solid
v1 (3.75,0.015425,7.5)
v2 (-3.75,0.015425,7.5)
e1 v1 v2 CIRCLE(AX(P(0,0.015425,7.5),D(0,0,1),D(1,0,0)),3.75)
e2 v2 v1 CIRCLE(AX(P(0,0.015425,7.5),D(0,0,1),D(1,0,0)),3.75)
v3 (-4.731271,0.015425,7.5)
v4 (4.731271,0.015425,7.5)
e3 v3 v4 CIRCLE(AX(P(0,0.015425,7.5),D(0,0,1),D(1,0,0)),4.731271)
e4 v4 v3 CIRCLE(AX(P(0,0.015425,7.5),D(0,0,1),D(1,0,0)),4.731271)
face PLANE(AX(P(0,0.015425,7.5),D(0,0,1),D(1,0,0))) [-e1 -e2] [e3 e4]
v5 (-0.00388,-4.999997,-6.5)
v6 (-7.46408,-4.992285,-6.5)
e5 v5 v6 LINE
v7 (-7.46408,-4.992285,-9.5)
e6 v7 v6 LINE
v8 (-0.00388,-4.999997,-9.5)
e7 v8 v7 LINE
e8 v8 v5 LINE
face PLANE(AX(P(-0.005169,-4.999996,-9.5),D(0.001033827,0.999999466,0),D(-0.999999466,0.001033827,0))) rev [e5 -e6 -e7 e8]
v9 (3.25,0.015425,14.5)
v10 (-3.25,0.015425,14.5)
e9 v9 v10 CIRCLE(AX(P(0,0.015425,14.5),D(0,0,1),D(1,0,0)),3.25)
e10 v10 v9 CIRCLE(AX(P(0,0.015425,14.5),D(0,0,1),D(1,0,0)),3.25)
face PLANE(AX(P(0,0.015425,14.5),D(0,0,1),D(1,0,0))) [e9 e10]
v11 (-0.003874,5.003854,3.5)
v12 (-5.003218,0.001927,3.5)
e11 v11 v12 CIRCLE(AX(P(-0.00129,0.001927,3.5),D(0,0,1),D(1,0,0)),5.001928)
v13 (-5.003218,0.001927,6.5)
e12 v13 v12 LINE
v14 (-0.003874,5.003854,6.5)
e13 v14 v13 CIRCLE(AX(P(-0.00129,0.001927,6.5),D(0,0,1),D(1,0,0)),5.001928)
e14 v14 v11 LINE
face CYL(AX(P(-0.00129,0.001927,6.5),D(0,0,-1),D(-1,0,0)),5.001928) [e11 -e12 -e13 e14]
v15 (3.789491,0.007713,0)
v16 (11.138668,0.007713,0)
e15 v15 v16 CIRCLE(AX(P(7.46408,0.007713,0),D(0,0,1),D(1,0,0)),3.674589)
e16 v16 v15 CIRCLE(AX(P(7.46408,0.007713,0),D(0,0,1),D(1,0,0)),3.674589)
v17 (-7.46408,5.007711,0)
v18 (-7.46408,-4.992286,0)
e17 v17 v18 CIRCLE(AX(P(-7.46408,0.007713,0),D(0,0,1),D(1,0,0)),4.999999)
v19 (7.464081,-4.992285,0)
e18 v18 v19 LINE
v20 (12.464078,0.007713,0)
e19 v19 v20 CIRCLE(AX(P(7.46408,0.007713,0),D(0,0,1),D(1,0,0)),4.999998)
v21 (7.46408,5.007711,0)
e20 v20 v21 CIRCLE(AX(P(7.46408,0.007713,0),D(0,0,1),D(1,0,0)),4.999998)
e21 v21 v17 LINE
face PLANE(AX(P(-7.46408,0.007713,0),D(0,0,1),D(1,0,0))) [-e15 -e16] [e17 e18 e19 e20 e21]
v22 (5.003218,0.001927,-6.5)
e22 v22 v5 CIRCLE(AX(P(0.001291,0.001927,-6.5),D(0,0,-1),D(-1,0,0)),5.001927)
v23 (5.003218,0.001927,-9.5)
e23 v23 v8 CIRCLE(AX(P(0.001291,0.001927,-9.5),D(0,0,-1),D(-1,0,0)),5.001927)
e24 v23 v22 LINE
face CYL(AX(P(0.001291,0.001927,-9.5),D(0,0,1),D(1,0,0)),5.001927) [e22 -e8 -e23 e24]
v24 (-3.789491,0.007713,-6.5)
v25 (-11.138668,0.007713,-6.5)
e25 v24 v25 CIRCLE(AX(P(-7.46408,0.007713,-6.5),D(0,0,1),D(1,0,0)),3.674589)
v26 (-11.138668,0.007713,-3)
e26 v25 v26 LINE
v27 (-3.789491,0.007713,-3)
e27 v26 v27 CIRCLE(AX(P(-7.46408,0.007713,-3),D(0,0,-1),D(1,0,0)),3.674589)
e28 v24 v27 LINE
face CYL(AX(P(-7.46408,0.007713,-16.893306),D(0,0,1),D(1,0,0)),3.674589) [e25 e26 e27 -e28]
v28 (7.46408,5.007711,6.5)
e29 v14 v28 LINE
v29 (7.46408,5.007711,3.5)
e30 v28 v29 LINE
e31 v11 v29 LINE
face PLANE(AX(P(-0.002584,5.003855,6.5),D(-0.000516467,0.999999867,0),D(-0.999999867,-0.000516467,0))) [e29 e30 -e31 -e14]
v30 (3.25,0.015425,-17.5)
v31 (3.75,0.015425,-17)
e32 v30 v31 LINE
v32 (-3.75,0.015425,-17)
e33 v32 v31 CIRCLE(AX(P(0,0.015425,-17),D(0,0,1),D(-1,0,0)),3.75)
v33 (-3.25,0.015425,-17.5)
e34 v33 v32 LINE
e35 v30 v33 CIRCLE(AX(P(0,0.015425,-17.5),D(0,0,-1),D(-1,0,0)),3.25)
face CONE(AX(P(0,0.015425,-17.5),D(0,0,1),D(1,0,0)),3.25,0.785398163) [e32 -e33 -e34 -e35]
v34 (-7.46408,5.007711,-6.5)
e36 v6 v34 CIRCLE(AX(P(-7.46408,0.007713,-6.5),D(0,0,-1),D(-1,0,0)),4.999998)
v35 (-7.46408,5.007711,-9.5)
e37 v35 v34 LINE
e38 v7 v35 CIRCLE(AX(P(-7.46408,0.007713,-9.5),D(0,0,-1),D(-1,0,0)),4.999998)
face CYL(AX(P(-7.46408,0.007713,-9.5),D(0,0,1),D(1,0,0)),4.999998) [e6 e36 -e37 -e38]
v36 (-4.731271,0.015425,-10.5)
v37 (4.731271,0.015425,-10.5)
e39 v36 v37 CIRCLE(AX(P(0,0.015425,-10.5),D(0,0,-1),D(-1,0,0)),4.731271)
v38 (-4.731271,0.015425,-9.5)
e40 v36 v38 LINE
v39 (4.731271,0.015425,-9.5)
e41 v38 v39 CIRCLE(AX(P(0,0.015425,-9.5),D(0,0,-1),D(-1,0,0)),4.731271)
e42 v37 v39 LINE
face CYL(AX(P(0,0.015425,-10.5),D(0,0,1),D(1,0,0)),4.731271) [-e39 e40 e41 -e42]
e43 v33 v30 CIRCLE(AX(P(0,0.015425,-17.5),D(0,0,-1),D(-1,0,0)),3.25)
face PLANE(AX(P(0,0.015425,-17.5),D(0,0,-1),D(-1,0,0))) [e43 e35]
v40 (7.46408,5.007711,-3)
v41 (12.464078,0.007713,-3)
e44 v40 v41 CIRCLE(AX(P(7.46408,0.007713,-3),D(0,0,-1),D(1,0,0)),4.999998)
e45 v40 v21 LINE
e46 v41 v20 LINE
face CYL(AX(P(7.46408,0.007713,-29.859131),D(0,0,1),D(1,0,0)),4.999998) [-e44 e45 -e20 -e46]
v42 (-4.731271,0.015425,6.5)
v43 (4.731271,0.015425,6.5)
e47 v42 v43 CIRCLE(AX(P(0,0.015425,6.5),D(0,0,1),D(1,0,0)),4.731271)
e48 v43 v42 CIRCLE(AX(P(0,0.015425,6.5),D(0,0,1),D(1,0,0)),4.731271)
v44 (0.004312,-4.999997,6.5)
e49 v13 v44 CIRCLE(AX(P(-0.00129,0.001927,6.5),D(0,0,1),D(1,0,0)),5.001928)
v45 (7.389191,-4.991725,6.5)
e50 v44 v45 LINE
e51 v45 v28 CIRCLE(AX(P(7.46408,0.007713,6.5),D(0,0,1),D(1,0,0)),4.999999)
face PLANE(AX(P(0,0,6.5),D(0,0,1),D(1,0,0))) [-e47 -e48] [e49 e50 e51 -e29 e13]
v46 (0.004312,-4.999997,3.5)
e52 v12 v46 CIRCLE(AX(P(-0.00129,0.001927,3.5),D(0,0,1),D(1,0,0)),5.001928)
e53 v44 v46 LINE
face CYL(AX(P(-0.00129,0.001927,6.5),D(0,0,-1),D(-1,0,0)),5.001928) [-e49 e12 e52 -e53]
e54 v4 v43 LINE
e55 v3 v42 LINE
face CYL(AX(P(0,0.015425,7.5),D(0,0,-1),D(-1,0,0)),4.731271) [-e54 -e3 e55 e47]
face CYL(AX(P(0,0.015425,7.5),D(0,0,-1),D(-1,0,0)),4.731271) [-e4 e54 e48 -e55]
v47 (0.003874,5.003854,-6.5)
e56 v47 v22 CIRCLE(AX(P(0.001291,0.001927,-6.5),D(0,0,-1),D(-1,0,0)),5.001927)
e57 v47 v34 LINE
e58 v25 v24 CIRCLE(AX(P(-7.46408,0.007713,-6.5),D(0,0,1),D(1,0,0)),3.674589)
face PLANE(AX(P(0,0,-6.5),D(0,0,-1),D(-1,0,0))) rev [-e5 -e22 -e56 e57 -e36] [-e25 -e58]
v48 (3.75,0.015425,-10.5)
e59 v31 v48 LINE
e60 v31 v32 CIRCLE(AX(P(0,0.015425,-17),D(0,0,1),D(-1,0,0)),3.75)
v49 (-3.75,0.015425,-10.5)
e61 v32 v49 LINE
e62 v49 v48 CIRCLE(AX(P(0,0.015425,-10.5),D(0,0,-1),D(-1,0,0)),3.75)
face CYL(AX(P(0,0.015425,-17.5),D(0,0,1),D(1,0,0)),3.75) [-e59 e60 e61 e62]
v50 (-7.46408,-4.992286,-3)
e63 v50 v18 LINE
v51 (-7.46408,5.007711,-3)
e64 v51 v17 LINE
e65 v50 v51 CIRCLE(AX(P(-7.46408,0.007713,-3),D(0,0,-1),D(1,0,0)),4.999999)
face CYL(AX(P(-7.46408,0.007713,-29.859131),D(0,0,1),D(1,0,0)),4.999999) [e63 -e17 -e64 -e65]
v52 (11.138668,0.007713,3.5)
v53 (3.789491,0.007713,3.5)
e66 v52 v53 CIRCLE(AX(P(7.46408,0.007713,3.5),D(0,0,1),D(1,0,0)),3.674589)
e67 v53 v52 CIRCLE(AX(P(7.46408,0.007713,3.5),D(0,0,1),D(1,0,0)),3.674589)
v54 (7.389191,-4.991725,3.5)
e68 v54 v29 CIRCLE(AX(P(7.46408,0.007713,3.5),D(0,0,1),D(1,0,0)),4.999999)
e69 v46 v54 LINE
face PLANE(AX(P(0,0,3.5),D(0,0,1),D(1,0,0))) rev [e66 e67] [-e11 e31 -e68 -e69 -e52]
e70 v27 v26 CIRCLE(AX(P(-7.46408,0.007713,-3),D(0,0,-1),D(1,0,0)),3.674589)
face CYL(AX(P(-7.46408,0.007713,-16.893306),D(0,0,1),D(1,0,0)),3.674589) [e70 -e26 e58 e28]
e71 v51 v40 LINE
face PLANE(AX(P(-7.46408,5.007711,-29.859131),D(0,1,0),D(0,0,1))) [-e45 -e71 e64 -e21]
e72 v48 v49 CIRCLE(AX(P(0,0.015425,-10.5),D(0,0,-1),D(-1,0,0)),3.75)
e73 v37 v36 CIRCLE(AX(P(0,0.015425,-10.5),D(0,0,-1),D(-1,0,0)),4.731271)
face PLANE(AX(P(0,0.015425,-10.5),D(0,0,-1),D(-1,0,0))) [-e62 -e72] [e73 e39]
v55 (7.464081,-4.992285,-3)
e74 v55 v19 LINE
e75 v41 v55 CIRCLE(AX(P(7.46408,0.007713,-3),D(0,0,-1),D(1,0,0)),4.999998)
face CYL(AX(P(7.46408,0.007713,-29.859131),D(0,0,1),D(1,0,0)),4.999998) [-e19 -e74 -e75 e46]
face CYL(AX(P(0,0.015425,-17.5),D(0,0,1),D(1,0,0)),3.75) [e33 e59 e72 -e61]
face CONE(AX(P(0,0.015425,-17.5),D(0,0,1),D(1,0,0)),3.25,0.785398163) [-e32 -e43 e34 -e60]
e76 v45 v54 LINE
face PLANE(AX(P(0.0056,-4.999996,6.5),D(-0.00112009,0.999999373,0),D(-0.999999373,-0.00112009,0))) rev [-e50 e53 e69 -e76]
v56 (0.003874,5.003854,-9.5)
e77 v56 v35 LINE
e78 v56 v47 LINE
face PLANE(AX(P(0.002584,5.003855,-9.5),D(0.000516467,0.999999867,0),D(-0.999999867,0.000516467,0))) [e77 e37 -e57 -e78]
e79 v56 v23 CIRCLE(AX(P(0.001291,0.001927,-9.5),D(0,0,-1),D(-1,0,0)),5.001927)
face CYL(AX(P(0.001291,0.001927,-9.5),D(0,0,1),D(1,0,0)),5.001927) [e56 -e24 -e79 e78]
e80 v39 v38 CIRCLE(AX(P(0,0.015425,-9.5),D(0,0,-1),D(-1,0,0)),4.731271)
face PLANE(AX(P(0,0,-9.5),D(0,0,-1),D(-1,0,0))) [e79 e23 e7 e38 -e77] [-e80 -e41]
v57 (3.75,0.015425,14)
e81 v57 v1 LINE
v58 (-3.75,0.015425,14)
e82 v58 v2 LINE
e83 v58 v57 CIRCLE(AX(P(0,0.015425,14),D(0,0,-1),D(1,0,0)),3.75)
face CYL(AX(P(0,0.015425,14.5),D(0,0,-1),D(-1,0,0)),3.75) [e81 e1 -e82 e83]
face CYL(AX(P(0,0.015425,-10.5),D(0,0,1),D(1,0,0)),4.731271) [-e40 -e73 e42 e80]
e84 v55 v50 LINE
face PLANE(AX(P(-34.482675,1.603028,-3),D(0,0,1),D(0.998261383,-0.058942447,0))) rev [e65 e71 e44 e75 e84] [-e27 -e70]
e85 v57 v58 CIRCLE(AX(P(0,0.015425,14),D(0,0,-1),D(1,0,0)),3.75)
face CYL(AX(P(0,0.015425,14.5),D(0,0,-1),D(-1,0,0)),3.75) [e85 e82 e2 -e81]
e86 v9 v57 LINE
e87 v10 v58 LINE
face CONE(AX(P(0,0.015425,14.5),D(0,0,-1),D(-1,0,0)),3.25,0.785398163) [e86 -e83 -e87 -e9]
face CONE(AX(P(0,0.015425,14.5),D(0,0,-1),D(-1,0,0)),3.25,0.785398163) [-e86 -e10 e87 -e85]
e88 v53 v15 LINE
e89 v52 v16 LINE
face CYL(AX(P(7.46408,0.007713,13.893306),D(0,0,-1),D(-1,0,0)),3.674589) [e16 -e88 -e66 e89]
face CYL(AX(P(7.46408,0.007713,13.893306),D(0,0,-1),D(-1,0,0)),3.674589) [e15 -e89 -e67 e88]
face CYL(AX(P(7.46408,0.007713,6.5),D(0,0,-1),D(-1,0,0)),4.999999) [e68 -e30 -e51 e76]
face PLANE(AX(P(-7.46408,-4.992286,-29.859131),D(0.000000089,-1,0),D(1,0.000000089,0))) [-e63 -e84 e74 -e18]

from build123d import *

# Parameters (mm, degrees)
BOSS_EXTRUDE7_DEPTH  = 3
SKETCH7_R            = 3.674588618
BOSS_EXTRUDE8_DEPTH  = 3.5
SKETCH8_R            = 3.674588618
BOSS_EXTRUDE9_DEPTH  = 3.5
SKETCH9_R            = 3.674588618
BOSS_EXTRUDE10_DEPTH = 3
SKETCH10_R           = 3.674588618
BOSS_EXTRUDE11_DEPTH = 3
SKETCH11_R           = 4.731271099
BOSS_EXTRUDE12_DEPTH = 1
SKETCH12_R           = 3.75
BOSS_EXTRUDE13_DEPTH = 7
BOSS_EXTRUDE14_START = 1
SKETCH13_R           = 4.731271099
BOSS_EXTRUDE14_DEPTH = 1
BOSS_EXTRUDE15_START = 7
SKETCH14_R           = 3.75
BOSS_EXTRUDE15_DEPTH = 7
CHAMFER1_SIZE        = 0.5


with BuildPart() as part:
    # Sketch1 → Boss-Extrude7 (new body)
    with BuildSketch(Plane.XY):
        with BuildLine():
            Line((-7.464079644, 5.007711231), (7.464079644, 5.007711231))
            ThreePointArc((7.464079644, 5.007711231), (12.46407809, 0.007713678), (7.464080538, -4.992284768))
            Line((7.464080538, -4.992284768), (-7.464079644, -4.992286102))
            ThreePointArc((-7.464079644, -4.992286102), (-12.464078311, 0.007712565), (-7.464079644, 5.007711231))
        make_face()
    extrude(amount=-BOSS_EXTRUDE7_DEPTH)

    # Sketch7 → Boss-Extrude8 (add)
    with BuildSketch(Plane(origin=(0, 0, -3), x_dir=(-1, 0, 0), z_dir=(0, 0, -1))):
        with Locations(Location((7.464079644, 0.007712565, 0), (0, 0, 180))):
            Circle(SKETCH7_R)
    extrude(amount=BOSS_EXTRUDE8_DEPTH)

    # Sketch8 → Boss-Extrude9 (add)
    with BuildSketch(Plane.XY):
        with Locations((7.464079644, 0.007712565)):
            Circle(SKETCH8_R)
    extrude(amount=BOSS_EXTRUDE9_DEPTH)

    # Sketch9 → Boss-Extrude10 (add)
    # profile 1 of 2: a face of its own
    with BuildSketch(Plane(origin=(0, 0, -6.5), x_dir=(-1, 0, 0), z_dir=(0, 0, -1))):
        with BuildLine():
            Line((7.458914982, 5.007708564), (-0.003874001, 5.003854283))
            ThreePointArc((-0.003874001, 5.003854283), (-5.003216645, -0.001949753), (0.003880454, -4.999997327))
            Line((0.003880454, -4.999997327), (7.464079644, -4.992284768))
            ThreePointArc((7.464079644, -4.992284768), (12.464077644, 0.007713232), (7.464079644, 5.007711231))
            Line((7.464079644, 5.007711231), (7.458914982, 5.007708564))
        make_face()
        with Locations(Location((7.464079644, 0.007712565, 0), (0, 0, 180))):
            Circle(SKETCH9_R, mode=Mode.SUBTRACT)
    # profile 2 of 2: a face of its own
    with BuildSketch(Plane(origin=(0, 0, -6.5), x_dir=(-1, 0, 0), z_dir=(0, 0, -1))):
        with Locations(Location((7.464079644, 0.007712565, 0), (0, 0, 180))):
            Circle(SKETCH9_R)
    extrude(amount=BOSS_EXTRUDE10_DEPTH)

    # Sketch10 → Boss-Extrude11 (add)
    # profile 1 of 2: a face of its own
    with BuildSketch(Plane.XY.offset(3.5)):
        with BuildLine():
            ThreePointArc((-0.003873651, 5.003854283), (-5.003216178, -0.00216555), (0.004312288, -4.999996973))
            Line((0.004312288, -4.999996973), (7.3891908, -4.991725236))
            ThreePointArc((7.3891908, -4.991725236), (12.463938092, -0.029732908), (7.464079644, 5.007711231))
            Line((7.464079644, 5.007711231), (7.458914981, 5.007708564))
            Line((7.458914981, 5.007708564), (-0.003873651, 5.003854283))
        make_face()
        with Locations((7.464079644, 0.007712565)):
            Circle(SKETCH10_R, mode=Mode.SUBTRACT)
    # profile 2 of 2: a face of its own
    with BuildSketch(Plane.XY.offset(3.5)):
        with Locations((7.464079644, 0.007712565)):
            Circle(SKETCH10_R)
    extrude(amount=BOSS_EXTRUDE11_DEPTH)

    # Sketch11 → Boss-Extrude12 (add)
    with BuildSketch(Plane.XY.offset(6.5)):
        with Locations((1e-09, 0.015425152)):
            Circle(SKETCH11_R)
    extrude(amount=BOSS_EXTRUDE12_DEPTH)

    # Sketch12 → Boss-Extrude13 (add)
    with BuildSketch(Plane.XY.offset(7.5)):
        with Locations((1e-09, 0.015425152)):
            Circle(SKETCH12_R)
    extrude(amount=BOSS_EXTRUDE13_DEPTH)

    # Sketch13 → Boss-Extrude14 (add)
    with BuildSketch(Plane(origin=(0, 0, -9.5), x_dir=(-1, 0, 0), z_dir=(0, 0, -1)).offset(BOSS_EXTRUDE14_START)):
        with Locations(Location((-1e-09, 0.015425152, 0), (0, 0, 180))):
            Circle(SKETCH13_R)
    extrude(amount=-BOSS_EXTRUDE14_DEPTH)

    # Sketch14 → Boss-Extrude15 (add)
    with BuildSketch(Plane(origin=(0, 0, -10.5), x_dir=(-1, 0, 0), z_dir=(0, 0, -1)).offset(BOSS_EXTRUDE15_START)):
        with Locations(Location((-1e-09, 0.015425152, 0), (0, 0, 180))):
            Circle(SKETCH14_R)
    extrude(amount=-BOSS_EXTRUDE15_DEPTH)

    # Chamfer1
    chamfer1_edges = [part.edges().sort_by_distance(p)[0] for p in [
        (-3.749999999, 0.015425152, 14.5),
        (-3.749999999, 0.015425152, -17.5),
    ]]
    chamfer(chamfer1_edges, length=CHAMFER1_SIZE)


solid = part.part
